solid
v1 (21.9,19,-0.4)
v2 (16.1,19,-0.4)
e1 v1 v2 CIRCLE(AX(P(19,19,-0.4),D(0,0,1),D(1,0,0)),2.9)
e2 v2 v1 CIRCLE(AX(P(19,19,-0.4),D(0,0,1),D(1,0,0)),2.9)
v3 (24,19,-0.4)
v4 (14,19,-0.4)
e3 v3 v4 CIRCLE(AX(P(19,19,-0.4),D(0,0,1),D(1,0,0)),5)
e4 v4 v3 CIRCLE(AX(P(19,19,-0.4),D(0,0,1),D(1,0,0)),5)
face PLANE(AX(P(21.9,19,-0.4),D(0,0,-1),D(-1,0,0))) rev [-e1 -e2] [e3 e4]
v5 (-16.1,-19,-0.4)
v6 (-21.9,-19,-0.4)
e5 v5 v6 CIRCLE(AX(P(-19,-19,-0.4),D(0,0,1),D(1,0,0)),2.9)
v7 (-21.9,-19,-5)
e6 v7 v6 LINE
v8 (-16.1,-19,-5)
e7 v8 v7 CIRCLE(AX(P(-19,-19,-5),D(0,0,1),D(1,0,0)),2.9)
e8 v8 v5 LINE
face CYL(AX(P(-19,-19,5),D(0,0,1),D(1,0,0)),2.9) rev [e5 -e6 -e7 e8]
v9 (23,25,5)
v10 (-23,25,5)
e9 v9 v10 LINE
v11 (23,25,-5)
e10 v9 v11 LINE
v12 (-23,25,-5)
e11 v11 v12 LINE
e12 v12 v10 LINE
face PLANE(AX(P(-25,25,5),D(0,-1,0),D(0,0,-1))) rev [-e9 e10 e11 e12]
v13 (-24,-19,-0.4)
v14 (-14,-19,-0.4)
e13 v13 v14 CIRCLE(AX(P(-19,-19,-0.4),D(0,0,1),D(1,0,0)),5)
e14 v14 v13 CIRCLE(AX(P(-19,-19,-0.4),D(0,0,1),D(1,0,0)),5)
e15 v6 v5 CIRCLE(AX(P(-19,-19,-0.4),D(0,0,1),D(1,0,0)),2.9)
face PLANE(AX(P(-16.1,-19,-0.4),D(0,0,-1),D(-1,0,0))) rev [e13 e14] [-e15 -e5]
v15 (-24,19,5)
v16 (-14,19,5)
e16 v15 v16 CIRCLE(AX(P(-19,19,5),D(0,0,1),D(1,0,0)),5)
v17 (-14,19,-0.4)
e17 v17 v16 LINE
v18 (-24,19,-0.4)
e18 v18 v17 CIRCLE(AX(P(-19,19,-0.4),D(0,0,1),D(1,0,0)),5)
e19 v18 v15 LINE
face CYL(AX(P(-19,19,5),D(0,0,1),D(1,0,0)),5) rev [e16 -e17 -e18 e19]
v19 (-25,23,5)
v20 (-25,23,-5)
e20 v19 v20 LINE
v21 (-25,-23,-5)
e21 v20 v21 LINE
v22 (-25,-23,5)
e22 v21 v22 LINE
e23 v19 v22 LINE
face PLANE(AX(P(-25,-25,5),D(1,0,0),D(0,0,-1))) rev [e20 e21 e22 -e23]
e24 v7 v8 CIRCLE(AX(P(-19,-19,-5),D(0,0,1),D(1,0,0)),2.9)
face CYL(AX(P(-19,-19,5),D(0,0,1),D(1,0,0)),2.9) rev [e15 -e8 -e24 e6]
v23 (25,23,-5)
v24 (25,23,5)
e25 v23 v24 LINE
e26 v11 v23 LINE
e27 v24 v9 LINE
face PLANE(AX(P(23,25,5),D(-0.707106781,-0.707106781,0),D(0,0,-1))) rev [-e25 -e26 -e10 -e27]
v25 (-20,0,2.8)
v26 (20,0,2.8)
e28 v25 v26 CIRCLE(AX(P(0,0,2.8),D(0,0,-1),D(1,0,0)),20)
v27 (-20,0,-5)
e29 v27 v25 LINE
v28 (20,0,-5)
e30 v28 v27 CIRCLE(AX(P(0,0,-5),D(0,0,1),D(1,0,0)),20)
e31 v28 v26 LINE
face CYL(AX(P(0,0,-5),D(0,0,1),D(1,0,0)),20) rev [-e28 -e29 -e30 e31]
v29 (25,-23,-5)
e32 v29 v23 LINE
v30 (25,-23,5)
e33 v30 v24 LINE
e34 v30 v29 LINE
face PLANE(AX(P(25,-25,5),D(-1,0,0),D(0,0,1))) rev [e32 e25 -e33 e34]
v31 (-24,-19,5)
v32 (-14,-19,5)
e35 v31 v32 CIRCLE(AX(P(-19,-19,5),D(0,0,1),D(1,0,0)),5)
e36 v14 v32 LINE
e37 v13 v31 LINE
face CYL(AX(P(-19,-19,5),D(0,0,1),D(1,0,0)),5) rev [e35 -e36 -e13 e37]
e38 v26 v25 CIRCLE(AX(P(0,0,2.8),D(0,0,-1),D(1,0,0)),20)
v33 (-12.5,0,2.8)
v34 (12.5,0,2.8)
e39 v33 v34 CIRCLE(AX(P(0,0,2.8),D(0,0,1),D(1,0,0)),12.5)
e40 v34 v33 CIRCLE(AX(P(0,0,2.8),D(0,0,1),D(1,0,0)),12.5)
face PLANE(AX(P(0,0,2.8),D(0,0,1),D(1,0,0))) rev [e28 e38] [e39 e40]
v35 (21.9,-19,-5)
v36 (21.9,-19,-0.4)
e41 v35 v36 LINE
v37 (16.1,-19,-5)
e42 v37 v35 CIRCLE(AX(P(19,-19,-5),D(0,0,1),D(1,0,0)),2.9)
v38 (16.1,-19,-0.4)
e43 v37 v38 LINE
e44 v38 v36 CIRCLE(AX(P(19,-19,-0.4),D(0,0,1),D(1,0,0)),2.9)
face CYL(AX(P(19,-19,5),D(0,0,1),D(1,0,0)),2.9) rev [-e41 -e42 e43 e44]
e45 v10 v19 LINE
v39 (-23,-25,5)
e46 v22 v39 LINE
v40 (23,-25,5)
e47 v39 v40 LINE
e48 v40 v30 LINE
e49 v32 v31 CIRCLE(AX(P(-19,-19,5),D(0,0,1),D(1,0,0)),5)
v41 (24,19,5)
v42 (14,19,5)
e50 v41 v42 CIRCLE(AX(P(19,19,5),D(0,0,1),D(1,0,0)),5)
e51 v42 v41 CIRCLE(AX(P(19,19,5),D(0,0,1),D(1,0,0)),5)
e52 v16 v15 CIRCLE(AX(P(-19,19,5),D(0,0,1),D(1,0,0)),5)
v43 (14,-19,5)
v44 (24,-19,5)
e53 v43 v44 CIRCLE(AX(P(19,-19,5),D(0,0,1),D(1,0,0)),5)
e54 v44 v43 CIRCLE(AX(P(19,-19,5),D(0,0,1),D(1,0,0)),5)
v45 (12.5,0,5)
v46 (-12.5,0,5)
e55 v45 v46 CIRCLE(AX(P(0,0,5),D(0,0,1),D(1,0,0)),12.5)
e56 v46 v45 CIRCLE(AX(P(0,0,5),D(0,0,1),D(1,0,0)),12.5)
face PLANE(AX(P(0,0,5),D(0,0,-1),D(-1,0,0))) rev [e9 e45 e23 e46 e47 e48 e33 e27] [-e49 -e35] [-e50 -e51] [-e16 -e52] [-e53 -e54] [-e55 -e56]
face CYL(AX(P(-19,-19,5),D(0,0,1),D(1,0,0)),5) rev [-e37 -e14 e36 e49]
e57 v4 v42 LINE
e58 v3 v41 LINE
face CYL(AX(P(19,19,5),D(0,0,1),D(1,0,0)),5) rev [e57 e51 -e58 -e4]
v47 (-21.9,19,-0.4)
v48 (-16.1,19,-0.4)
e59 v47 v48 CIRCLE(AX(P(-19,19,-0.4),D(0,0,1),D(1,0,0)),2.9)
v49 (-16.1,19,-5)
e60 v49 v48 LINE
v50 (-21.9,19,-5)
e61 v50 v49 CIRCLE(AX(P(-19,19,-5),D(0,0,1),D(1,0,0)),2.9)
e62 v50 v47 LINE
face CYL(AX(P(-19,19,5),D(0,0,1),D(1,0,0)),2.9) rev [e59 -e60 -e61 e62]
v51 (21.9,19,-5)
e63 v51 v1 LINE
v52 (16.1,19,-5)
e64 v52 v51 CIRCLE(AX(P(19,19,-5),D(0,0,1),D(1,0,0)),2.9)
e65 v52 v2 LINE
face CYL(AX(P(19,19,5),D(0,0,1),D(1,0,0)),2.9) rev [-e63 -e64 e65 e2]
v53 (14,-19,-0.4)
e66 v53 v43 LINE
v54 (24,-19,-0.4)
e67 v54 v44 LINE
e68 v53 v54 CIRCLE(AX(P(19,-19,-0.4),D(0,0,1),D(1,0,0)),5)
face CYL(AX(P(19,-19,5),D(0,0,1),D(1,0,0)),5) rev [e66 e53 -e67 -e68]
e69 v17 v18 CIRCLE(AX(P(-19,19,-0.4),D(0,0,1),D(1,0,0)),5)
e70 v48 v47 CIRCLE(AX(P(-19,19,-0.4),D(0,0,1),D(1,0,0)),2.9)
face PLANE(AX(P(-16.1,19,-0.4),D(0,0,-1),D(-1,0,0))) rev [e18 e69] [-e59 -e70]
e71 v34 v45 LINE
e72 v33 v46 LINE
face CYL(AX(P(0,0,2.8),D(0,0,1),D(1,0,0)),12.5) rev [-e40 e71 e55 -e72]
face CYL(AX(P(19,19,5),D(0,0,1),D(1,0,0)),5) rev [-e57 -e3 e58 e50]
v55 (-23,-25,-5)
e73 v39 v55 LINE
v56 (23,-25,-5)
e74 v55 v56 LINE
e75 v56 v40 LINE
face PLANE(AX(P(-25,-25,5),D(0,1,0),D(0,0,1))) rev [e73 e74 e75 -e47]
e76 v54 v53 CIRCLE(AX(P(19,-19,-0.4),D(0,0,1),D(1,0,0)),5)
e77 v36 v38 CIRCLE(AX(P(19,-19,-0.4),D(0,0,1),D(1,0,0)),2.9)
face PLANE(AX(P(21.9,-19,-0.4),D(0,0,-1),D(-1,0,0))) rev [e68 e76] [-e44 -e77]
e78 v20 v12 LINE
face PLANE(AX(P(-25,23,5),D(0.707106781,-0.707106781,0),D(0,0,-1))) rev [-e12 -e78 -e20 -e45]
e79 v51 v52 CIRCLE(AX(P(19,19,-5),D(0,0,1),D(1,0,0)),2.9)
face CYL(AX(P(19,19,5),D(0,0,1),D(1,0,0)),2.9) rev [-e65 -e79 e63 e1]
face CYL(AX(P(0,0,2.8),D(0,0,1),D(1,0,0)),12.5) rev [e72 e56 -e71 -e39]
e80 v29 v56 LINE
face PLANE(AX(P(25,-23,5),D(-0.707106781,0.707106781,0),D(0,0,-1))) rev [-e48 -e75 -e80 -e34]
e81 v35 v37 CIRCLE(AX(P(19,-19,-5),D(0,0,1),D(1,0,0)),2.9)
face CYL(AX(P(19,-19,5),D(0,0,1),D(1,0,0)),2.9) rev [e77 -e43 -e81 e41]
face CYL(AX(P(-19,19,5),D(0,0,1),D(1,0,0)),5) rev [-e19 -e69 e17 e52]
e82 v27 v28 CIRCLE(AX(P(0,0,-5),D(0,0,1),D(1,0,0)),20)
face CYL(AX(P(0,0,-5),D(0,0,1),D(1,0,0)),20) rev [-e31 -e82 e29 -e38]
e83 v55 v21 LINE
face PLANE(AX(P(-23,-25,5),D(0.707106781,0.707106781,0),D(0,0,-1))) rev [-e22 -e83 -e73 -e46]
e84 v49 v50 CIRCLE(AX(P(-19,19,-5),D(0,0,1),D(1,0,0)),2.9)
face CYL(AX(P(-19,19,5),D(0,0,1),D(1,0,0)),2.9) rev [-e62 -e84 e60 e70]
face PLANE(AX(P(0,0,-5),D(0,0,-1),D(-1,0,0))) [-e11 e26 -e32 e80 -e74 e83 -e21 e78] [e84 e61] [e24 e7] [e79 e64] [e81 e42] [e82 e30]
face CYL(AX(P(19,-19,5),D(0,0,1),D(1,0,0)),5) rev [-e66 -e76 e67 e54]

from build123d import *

# Parameters (mm, degrees)
SKETCH_1_W                   = 50
SKETCH_1_H                   = 50
EXTRUDE_1_DEPTH              = 5
SKETCH_2_R                   = 20
CUT_EXTRUDE_1_DEPTH          = 37.742346142
HOLE_WIZARD_M5_1_D           = 5.8
HOLE_WIZARD_M5_1_CBORE_D     = 10
HOLE_WIZARD_M5_1_CBORE_DEPTH = 5.4
CHAMFER_1_SIZE               = 2
SKETCH_7_R                   = 20
SKETCH_7_R_2                 = 12.5
EXTRUDE_2_DEPTH              = 2.2


with BuildPart() as part:
    # 草图1 → 凸台-拉伸1 (new, symmetric)
    with BuildSketch(Plane.XY):
        Rectangle(SKETCH_1_W, SKETCH_1_H)
    extrude(amount=EXTRUDE_1_DEPTH, both=True)

    # 草图2 → 切除-拉伸1 (cut, through all)
    with BuildSketch(Plane.XY.offset(5)):
        Circle(SKETCH_2_R)
    extrude(amount=-CUT_EXTRUDE_1_DEPTH, mode=Mode.SUBTRACT)

    # M5 六角凹头螺钉的柱形沉头孔1 (through all)
    with Locations(Plane.XY.offset(5)):
        with Locations((-19, 19), (19, 19), (-19, -19), (19, -19)):
            CounterBoreHole(HOLE_WIZARD_M5_1_D / 2, HOLE_WIZARD_M5_1_CBORE_D / 2, HOLE_WIZARD_M5_1_CBORE_DEPTH)

    # 倒角1
    chamfer_1_edges = [part.edges().sort_by_distance(p)[0] for p in [
        (25, -25, 0),
        (-25, -25, 0),
        (-25, 25, 0),
        (25, 25, 0),
    ]]
    chamfer(chamfer_1_edges, length=CHAMFER_1_SIZE)

    # 草图7 → 凸台-拉伸2 (add)
    with BuildSketch(Plane.XY.offset(5)):
        Circle(SKETCH_7_R)
        Circle(SKETCH_7_R_2, mode=Mode.SUBTRACT)
    extrude(amount=-EXTRUDE_2_DEPTH)


solid = part.part
